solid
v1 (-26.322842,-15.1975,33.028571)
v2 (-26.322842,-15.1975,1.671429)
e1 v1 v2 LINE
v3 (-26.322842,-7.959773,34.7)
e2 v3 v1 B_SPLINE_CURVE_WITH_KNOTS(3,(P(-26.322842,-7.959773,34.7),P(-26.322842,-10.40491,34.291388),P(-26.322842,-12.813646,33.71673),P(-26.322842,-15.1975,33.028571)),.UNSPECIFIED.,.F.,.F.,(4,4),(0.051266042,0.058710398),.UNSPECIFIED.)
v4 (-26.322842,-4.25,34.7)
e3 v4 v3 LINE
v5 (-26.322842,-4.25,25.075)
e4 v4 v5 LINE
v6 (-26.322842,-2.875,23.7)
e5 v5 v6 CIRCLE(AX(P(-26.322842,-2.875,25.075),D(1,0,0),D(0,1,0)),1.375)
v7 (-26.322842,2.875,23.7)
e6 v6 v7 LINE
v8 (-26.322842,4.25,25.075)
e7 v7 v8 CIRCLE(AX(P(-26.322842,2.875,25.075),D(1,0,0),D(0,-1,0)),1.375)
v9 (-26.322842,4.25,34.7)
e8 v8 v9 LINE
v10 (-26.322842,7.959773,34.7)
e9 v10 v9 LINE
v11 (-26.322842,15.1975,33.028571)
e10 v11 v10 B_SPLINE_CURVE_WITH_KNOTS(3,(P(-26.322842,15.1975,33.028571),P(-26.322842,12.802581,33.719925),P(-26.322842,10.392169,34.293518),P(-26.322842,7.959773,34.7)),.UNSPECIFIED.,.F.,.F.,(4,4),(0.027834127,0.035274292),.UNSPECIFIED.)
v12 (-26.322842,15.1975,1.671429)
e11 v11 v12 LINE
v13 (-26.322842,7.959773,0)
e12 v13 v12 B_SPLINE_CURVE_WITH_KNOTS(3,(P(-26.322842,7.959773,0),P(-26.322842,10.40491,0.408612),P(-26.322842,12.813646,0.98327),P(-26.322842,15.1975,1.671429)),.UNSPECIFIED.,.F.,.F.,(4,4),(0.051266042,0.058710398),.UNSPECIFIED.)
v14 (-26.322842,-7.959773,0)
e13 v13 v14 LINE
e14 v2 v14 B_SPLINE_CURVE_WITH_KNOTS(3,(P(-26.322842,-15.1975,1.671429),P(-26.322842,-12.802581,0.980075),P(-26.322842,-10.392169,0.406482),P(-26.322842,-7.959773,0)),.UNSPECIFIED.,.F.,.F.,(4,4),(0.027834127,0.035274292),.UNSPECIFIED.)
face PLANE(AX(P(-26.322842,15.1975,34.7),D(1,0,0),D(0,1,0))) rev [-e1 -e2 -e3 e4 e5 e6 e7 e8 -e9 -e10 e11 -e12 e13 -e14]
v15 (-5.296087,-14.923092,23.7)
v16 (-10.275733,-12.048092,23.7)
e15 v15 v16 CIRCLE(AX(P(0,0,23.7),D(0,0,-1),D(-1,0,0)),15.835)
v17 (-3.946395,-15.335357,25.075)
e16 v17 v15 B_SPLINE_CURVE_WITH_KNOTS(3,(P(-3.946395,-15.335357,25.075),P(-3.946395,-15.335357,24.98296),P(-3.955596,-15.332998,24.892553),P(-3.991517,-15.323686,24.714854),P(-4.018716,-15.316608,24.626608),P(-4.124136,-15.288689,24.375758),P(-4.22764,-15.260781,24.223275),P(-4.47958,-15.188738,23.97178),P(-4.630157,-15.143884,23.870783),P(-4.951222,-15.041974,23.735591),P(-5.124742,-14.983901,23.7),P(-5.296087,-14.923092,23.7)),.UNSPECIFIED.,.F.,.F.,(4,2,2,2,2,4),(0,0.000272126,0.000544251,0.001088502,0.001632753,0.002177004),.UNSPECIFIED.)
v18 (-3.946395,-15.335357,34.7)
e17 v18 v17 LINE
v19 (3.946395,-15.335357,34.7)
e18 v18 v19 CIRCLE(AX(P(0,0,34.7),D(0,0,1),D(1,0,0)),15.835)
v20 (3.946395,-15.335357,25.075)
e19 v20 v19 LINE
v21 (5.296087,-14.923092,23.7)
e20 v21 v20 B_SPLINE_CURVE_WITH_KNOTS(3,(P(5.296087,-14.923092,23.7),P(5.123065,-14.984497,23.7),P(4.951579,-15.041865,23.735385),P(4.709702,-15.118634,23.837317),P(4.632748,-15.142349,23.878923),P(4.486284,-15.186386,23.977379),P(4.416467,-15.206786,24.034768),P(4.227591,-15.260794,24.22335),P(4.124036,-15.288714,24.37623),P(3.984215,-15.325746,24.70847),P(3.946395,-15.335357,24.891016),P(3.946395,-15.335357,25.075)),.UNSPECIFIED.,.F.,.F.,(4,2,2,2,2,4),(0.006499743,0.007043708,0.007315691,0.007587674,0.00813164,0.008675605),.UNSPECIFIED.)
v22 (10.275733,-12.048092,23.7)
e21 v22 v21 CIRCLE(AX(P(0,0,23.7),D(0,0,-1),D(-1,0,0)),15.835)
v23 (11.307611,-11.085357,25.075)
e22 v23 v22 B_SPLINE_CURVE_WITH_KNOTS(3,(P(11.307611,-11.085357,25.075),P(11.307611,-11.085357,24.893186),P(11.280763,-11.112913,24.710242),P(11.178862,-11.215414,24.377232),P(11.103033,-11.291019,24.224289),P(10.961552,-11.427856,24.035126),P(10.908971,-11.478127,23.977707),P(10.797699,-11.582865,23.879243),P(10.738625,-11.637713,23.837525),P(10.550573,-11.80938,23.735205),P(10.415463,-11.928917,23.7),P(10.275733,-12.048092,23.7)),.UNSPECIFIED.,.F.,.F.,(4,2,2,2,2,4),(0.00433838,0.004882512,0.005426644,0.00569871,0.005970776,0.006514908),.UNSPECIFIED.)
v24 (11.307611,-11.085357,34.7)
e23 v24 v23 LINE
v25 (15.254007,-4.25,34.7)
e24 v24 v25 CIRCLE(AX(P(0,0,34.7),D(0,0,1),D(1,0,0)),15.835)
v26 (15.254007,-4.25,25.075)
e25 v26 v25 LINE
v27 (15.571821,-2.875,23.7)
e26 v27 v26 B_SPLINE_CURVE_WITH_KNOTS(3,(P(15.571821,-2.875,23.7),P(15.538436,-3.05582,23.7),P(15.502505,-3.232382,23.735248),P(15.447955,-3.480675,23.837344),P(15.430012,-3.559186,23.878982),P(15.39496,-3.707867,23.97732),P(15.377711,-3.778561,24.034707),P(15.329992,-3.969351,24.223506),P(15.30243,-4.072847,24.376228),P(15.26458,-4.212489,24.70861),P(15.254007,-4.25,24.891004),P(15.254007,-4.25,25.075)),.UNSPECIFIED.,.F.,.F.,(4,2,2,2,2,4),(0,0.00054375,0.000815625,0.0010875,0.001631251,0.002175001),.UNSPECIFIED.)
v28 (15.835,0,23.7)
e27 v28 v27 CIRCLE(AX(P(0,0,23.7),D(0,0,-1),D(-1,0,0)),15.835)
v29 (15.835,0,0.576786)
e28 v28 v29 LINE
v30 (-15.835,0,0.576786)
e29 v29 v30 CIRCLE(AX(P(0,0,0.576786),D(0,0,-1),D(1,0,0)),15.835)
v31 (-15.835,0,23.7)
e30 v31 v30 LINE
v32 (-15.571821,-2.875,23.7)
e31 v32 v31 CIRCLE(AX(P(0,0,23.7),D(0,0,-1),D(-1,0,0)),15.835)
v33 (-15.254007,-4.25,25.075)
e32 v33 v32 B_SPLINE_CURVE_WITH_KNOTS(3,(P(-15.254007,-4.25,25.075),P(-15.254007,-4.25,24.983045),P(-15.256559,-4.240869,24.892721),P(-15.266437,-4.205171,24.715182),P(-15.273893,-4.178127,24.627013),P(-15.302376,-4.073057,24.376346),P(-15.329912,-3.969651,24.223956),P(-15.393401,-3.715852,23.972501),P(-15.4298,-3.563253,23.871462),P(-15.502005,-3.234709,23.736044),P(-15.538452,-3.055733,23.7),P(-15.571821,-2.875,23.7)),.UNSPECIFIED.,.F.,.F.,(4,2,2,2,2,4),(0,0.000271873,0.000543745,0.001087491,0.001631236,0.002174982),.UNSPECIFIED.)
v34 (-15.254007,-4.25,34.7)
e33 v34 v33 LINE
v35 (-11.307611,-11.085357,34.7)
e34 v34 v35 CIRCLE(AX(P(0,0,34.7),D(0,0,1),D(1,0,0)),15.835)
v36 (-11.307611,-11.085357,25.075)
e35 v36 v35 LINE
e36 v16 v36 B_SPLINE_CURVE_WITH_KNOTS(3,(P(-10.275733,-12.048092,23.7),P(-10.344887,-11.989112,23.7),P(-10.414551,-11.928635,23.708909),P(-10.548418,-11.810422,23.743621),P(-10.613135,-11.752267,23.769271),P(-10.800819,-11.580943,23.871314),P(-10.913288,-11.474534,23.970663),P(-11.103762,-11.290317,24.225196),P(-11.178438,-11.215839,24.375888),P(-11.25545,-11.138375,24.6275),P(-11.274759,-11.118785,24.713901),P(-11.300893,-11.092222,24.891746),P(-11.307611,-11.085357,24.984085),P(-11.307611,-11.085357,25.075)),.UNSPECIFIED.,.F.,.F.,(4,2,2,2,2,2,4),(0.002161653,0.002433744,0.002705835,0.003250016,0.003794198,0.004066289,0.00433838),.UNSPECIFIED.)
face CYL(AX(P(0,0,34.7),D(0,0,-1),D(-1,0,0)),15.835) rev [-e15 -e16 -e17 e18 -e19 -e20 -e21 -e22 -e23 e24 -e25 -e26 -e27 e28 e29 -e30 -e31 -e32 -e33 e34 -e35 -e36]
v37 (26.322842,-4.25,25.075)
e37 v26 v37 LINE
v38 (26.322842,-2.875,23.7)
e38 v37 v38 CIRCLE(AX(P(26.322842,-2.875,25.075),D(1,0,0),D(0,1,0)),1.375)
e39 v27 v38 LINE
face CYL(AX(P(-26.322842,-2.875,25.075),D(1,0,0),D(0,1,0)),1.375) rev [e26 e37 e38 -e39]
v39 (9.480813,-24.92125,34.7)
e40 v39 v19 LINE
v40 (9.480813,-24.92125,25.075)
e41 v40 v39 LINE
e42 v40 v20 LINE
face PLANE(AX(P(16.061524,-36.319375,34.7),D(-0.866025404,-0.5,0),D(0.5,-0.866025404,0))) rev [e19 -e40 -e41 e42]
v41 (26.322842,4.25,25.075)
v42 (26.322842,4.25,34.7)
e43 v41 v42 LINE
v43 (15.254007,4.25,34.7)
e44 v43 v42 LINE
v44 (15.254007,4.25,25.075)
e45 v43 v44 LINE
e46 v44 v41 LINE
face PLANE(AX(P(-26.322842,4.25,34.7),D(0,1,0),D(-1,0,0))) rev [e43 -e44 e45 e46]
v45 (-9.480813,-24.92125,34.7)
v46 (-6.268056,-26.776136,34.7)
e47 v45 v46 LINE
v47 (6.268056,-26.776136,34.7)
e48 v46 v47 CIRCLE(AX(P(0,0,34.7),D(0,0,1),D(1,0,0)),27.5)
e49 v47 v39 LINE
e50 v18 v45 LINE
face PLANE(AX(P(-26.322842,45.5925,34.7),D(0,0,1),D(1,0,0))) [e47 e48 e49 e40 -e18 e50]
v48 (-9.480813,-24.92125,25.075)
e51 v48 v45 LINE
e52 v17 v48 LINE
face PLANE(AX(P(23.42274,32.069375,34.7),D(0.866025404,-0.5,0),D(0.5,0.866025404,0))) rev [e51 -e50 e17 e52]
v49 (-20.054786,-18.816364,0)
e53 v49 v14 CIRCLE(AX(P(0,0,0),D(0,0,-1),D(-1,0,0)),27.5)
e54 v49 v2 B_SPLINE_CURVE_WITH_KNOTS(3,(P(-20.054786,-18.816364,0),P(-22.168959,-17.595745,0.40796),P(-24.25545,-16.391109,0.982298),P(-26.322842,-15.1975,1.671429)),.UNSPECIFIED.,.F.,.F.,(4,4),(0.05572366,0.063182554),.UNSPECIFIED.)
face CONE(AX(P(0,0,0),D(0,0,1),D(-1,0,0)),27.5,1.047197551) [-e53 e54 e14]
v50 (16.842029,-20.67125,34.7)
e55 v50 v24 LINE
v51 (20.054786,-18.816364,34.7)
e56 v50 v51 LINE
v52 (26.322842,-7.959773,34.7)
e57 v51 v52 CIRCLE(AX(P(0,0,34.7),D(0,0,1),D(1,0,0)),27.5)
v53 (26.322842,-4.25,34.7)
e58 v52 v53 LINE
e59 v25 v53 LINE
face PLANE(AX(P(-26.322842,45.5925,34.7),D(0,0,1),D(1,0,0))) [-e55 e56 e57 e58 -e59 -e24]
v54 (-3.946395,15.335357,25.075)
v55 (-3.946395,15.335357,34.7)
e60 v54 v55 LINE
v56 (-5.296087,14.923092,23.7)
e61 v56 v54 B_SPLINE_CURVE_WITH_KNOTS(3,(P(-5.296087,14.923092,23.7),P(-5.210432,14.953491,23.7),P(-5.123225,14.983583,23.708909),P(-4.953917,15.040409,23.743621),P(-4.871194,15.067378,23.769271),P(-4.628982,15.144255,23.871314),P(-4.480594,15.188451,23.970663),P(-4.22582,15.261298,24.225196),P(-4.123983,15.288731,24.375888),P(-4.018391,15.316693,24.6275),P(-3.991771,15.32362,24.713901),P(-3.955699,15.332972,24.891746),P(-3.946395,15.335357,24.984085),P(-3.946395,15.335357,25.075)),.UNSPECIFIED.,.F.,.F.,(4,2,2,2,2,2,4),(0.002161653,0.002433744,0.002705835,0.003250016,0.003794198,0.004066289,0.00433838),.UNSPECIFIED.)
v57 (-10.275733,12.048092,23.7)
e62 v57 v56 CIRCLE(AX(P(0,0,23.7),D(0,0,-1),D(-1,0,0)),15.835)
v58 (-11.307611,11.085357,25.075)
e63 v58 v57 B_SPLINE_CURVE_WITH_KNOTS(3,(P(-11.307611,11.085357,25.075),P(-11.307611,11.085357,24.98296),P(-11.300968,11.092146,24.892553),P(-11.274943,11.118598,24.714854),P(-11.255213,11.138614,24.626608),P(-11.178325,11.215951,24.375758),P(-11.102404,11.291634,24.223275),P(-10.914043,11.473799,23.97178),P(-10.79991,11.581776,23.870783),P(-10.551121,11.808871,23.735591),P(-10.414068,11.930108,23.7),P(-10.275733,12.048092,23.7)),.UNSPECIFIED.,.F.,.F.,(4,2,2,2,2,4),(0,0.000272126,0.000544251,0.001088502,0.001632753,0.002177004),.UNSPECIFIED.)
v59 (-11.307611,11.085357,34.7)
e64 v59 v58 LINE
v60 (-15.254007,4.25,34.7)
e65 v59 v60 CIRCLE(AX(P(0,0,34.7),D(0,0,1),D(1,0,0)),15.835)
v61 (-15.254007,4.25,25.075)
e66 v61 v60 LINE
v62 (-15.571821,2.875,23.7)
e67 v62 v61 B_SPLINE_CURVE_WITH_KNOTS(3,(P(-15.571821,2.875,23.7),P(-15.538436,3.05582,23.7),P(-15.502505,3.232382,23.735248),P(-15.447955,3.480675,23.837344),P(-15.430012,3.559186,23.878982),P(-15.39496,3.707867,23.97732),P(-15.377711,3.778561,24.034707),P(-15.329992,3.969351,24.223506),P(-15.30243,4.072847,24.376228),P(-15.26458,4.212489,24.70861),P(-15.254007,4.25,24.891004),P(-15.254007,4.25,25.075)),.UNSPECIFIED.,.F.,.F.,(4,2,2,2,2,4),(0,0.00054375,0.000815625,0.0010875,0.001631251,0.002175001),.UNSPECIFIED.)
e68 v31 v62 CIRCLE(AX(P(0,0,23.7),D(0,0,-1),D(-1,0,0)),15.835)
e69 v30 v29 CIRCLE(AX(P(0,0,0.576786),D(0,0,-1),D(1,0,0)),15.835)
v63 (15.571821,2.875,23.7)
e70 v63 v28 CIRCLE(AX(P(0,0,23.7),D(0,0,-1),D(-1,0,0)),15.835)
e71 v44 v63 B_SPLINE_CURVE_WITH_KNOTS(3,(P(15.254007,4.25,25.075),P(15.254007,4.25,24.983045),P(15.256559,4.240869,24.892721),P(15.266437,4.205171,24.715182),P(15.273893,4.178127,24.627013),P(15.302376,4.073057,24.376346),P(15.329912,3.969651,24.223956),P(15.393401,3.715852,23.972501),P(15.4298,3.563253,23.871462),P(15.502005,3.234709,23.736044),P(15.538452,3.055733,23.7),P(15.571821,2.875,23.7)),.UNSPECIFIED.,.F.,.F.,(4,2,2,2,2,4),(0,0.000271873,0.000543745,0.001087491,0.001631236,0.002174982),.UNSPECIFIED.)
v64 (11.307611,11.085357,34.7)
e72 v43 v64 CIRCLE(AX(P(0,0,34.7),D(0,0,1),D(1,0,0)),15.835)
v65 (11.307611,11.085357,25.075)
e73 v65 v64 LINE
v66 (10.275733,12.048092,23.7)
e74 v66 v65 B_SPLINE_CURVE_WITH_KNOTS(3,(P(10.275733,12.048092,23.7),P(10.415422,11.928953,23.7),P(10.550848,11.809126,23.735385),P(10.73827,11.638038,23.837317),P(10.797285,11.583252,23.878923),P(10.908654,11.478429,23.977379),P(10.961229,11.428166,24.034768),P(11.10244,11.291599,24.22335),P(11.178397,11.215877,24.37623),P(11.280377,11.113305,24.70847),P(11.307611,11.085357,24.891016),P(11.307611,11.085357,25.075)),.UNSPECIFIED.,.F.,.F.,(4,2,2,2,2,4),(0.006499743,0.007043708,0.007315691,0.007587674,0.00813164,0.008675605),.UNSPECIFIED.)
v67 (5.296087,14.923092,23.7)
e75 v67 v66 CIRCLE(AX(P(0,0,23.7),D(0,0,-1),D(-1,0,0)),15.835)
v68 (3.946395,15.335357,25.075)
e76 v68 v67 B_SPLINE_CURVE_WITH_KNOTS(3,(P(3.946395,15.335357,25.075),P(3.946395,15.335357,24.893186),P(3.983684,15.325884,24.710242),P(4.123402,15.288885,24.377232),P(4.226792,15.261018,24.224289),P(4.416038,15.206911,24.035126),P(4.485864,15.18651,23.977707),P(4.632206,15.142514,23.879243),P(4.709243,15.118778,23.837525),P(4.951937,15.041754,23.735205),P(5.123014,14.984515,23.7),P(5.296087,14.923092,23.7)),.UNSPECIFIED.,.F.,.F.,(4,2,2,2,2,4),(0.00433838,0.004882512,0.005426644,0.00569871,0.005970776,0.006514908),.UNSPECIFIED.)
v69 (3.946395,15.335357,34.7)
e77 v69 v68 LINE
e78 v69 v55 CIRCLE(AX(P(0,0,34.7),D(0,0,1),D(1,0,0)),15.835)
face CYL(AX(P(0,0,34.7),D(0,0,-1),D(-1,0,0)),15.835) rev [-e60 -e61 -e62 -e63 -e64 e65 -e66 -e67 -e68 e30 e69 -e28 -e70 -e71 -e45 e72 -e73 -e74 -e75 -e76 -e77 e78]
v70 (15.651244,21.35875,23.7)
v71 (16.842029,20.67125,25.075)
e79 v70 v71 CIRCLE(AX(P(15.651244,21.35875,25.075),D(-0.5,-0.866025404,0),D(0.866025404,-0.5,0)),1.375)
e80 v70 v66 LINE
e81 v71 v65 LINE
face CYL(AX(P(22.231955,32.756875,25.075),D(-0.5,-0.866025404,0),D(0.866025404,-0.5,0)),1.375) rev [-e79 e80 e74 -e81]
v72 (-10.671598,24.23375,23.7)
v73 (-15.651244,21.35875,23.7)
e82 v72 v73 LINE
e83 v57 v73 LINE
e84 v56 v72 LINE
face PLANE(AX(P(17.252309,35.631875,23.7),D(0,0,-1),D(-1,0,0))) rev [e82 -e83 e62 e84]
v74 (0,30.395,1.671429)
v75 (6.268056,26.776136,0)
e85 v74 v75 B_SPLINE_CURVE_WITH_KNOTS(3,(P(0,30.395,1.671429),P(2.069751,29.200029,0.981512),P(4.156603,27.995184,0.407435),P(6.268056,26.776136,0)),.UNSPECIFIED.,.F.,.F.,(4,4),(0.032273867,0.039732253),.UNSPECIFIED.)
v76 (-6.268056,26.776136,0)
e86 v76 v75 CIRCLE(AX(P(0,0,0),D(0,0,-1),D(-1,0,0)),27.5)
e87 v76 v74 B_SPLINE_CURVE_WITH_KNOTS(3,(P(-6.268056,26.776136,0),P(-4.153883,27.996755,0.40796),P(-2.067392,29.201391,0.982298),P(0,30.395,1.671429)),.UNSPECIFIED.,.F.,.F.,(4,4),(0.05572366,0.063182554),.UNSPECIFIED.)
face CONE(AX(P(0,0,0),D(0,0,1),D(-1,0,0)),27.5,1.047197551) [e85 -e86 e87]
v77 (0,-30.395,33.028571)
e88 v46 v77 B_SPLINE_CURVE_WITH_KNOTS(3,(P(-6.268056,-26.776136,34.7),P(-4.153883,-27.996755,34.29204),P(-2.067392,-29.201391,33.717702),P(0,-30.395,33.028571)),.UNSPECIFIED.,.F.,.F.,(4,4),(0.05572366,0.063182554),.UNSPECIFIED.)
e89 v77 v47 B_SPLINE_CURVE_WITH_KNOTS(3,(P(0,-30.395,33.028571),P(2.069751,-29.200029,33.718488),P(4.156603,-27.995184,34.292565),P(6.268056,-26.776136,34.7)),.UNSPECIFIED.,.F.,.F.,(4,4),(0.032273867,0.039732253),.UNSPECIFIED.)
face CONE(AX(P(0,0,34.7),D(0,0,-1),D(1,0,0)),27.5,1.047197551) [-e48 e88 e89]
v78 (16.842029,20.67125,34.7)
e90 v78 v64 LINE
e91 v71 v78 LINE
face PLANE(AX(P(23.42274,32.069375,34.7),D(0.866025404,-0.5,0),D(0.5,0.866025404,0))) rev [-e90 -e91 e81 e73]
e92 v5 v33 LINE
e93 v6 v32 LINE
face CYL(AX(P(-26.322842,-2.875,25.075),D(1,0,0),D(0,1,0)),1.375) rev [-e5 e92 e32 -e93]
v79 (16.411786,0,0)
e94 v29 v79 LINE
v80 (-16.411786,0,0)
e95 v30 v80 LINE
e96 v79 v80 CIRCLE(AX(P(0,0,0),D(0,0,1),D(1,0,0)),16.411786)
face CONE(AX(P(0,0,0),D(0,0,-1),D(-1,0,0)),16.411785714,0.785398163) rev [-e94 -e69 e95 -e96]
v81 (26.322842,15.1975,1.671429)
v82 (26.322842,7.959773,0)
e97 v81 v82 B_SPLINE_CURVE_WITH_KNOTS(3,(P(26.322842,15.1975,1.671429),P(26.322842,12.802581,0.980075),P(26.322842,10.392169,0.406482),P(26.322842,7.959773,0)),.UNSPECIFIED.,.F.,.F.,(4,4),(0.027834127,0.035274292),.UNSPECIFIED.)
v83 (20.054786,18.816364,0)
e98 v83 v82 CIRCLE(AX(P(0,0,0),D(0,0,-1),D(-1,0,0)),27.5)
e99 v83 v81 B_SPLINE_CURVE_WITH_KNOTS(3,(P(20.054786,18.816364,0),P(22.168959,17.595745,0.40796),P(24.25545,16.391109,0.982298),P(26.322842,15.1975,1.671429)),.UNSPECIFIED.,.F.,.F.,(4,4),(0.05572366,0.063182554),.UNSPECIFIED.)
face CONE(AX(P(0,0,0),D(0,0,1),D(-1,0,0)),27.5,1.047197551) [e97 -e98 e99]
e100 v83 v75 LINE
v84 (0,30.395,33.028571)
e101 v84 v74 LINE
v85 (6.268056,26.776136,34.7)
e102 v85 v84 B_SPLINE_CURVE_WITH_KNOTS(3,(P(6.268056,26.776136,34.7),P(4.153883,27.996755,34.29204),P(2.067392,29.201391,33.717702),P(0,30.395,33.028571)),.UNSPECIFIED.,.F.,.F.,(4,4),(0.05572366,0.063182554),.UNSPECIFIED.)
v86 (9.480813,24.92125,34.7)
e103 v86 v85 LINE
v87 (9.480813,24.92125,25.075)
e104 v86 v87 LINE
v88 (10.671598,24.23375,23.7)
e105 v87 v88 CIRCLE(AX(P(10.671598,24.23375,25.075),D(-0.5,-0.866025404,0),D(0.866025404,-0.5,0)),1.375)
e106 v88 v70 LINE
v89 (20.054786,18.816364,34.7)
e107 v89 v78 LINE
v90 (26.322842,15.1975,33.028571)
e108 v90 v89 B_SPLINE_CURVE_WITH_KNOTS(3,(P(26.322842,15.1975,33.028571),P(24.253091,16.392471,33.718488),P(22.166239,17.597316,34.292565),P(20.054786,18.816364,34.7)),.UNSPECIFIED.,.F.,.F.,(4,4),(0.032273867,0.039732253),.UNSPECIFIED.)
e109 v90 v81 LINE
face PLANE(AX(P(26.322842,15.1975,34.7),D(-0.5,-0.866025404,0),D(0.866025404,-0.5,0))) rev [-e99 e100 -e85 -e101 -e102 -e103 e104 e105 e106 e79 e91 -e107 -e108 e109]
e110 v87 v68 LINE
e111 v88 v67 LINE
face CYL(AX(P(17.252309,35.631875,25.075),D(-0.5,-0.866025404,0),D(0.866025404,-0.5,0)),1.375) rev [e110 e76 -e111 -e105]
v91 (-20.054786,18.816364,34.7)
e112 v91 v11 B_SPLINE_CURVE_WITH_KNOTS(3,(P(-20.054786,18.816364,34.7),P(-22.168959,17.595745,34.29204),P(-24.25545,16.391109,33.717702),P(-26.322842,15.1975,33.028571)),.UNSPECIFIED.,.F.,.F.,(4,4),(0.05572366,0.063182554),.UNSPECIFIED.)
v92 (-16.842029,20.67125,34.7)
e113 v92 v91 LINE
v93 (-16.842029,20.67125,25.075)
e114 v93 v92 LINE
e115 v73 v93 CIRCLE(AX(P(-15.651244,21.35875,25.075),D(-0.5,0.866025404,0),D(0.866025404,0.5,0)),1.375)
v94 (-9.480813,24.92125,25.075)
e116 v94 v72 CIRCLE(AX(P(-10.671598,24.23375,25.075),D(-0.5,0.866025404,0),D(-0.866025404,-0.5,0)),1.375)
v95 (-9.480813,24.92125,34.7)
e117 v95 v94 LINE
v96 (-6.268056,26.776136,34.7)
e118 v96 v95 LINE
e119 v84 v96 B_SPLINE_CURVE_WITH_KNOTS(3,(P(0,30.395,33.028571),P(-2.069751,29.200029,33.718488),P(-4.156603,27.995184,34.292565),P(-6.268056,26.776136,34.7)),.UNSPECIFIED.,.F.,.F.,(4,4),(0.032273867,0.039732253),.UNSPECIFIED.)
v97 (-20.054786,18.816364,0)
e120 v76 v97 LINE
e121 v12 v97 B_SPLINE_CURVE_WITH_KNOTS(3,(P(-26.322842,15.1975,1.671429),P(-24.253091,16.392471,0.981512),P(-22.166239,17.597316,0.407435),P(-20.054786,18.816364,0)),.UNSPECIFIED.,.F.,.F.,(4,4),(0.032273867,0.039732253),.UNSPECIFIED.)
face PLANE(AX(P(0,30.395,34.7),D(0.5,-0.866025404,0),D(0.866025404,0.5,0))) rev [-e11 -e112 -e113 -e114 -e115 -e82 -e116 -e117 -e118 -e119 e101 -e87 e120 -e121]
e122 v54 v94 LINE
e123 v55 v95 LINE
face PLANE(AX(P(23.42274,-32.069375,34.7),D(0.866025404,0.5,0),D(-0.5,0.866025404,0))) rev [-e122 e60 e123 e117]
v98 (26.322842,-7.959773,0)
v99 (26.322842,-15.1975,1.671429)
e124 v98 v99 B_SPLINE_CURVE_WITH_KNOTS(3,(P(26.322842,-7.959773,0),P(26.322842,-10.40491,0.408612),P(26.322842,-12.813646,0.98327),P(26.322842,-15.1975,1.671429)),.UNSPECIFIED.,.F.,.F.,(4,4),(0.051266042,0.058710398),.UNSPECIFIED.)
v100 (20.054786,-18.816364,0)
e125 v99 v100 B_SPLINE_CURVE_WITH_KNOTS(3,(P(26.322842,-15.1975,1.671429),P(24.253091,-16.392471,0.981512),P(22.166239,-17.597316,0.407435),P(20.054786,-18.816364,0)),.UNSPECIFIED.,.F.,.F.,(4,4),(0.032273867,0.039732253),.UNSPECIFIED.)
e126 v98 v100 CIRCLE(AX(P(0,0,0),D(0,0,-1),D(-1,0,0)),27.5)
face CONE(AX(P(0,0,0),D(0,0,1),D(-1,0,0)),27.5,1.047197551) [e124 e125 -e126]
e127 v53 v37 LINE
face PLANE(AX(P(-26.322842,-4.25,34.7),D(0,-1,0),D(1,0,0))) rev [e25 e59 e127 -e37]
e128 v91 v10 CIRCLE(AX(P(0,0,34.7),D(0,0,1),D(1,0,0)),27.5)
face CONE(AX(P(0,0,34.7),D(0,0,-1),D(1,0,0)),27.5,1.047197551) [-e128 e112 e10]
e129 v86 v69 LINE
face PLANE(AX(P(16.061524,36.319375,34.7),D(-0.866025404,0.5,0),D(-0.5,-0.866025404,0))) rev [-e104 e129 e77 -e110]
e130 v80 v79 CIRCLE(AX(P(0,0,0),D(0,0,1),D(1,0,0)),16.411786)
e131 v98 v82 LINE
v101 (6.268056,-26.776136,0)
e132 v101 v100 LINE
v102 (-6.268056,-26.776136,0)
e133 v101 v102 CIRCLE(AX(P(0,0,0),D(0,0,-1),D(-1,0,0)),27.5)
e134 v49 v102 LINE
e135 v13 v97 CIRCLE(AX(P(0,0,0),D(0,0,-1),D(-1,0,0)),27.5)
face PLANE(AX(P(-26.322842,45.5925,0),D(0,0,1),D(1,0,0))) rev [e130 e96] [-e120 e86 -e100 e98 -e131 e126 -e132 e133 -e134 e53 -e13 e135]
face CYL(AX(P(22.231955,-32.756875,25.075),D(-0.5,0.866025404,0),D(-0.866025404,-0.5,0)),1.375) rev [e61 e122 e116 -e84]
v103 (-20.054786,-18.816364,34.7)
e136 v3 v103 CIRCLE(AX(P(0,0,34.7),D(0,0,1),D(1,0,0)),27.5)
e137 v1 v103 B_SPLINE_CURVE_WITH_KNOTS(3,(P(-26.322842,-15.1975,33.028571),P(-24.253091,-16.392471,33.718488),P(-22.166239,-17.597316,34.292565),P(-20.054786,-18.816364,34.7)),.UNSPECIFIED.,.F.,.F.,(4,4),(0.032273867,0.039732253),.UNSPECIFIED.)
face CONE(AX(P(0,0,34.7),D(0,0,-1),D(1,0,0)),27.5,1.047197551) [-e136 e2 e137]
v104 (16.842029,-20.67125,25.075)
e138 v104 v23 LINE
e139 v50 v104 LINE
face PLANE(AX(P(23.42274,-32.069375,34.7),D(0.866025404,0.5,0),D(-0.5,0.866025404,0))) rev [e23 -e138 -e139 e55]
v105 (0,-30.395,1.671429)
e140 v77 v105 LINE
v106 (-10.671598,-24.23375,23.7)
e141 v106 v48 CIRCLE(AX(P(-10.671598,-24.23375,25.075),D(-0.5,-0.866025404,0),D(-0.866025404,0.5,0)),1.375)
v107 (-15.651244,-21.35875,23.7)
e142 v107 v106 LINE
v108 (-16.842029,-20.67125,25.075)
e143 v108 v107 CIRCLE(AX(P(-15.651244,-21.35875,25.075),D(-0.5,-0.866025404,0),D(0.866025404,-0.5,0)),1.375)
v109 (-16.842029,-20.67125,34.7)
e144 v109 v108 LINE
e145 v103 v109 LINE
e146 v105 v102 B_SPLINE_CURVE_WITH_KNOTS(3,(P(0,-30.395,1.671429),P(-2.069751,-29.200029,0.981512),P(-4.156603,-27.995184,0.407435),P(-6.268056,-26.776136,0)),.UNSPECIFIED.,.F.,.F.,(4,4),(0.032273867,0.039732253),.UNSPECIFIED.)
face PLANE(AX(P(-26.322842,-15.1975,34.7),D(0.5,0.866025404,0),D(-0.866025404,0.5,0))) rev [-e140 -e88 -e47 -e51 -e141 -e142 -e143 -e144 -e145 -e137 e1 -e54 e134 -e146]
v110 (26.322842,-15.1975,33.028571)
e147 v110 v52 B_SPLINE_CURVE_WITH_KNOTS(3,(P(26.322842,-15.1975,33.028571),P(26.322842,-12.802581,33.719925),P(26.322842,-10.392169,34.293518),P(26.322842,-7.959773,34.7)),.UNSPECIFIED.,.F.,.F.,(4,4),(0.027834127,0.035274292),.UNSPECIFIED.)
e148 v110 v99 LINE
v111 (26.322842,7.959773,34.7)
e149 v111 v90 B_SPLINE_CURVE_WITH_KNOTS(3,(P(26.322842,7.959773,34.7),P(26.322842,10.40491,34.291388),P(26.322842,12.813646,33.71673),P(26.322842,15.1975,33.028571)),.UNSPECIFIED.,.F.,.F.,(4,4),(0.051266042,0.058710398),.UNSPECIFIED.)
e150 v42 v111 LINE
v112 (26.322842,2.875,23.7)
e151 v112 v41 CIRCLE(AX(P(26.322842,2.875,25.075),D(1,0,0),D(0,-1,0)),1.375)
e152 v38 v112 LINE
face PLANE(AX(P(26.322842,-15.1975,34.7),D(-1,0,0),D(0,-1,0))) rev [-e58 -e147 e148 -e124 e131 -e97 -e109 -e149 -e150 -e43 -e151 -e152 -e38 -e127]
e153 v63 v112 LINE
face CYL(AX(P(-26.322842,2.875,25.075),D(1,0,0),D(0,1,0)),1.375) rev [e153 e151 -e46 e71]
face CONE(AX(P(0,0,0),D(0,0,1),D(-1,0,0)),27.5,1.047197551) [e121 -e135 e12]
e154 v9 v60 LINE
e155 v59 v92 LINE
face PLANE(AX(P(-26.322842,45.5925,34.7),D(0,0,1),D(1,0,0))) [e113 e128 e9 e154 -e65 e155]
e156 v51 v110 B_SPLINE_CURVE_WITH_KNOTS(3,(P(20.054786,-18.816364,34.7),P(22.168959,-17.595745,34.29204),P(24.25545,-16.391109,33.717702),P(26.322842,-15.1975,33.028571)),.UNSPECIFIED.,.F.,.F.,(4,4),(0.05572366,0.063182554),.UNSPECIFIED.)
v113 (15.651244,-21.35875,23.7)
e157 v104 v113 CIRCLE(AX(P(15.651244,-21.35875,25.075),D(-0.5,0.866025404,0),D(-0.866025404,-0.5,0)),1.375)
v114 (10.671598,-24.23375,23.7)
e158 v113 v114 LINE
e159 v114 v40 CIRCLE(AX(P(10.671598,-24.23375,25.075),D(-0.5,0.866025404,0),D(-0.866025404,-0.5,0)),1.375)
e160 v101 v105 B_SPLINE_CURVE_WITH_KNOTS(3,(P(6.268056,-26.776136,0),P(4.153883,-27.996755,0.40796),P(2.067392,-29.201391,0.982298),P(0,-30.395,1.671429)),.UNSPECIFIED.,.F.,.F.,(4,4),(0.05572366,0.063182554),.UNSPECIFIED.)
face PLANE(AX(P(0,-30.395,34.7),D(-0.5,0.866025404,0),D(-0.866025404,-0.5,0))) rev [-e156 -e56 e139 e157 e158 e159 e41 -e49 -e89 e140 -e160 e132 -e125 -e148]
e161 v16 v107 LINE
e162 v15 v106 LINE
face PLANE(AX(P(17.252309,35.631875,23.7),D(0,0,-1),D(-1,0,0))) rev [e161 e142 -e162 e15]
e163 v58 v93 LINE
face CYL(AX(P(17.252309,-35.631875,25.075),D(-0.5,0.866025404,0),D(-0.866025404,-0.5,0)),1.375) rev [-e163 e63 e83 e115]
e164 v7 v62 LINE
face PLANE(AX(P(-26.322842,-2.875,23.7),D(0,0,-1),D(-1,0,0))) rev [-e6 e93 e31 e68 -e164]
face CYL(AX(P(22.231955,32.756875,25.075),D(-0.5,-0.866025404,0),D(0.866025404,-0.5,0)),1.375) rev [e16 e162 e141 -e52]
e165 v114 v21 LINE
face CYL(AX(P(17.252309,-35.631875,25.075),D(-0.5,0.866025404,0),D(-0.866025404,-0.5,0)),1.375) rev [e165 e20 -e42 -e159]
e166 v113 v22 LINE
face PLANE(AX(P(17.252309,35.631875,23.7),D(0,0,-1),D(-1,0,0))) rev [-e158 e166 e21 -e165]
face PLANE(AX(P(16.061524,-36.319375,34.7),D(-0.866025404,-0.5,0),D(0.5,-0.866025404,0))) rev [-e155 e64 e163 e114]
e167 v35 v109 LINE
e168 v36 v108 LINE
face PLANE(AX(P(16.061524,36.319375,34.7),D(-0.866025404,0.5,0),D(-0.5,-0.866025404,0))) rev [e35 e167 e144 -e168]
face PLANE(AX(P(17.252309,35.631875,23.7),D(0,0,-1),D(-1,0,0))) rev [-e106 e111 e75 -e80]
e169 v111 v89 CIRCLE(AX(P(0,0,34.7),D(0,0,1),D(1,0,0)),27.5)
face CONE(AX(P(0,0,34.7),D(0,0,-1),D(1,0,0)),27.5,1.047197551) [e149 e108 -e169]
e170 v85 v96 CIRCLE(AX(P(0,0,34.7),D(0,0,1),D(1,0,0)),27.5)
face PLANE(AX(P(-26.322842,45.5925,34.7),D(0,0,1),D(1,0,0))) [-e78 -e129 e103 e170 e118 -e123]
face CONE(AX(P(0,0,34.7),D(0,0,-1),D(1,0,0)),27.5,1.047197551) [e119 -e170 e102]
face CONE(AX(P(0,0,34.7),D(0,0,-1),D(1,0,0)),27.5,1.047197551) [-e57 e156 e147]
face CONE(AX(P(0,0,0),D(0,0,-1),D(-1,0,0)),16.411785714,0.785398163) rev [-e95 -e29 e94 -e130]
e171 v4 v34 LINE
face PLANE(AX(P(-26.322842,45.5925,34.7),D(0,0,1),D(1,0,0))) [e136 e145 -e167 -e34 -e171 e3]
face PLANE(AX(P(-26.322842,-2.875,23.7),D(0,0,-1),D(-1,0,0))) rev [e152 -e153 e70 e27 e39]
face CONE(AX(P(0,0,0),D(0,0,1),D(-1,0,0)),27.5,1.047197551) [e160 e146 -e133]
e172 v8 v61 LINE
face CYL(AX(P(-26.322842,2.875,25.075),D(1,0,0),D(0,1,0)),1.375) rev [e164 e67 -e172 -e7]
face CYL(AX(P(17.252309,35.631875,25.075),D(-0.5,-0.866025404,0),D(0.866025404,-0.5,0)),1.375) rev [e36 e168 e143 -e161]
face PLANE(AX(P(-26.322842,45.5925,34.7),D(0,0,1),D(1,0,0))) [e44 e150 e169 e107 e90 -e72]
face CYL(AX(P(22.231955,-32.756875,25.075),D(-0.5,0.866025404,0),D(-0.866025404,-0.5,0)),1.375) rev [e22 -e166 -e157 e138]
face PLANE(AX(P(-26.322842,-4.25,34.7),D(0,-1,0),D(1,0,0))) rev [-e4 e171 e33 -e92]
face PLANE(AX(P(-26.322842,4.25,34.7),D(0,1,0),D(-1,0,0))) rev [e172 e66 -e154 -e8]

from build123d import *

# Parameters (mm, degrees)
SKETCH_1_R               = 15.835
EXTRUDE_848_DEPTH        = 34.7
SKETCH_2_OUTSIDE_W       = 259.61
SKETCH_2_OUTSIDE_H       = 267.754
SKETCH_2_OUTSIDE_R       = 27.5
CUT_EXTRUDE_1_DEPTH      = 54.111562242
CUT_EXTRUDE_1_DRAFT      = -60
SKETCH_3_OUTSIDE_W       = 259.61
SKETCH_3_OUTSIDE_H       = 267.754
SKETCH_3_OUTSIDE_R       = 27.5
CUT_EXTRUDE_2_DEPTH      = 54.111562242
CUT_EXTRUDE_2_DRAFT      = -60
CUT_EXTRUDE_3_DEPTH      = 70.9965292
PATTERN_CIRCULAR_1_COUNT = 3
CHAMFER_1_SIZE           = 0.576785714


with BuildPart() as part:
    # 草图1 → Extrude 848 (new body)
    with BuildSketch(Plane.XY):
        Polygon((0, 30.395), (-26.322842148, 15.1975), (-26.322842148, -15.1975), (0, -30.395), (26.322842148, -15.1975), (26.322842148, 15.1975), align=None)
        Circle(SKETCH_1_R, mode=Mode.SUBTRACT)
    extrude(amount=EXTRUDE_848_DEPTH)


with BuildPart() as cut_extrude_1_tool:
    # 草图2 outside → 切除-拉伸1 (with draft: the straight prism first)
    with BuildSketch(Plane(origin=(0, 0, 0), x_dir=(-1, 0, 0), z_dir=(0, 0, -1))):
        Rectangle(SKETCH_2_OUTSIDE_W, SKETCH_2_OUTSIDE_H)
        Circle(SKETCH_2_OUTSIDE_R, mode=Mode.SUBTRACT)
    extrude(amount=-CUT_EXTRUDE_1_DEPTH)
    # 切除-拉伸1: the draft: its side faces are tilted about the plane it starts from
    cut_extrude_1_sides = [cut_extrude_1_tool.faces().sort_by_distance(p)[0] for p in [
        (0, -133.877, 27.055781121),
        (-129.805, 0, 27.055781121),
        (0, 133.877, 27.055781121),
        (129.805, 0, 27.055781121),
        (27.5, 0, 27.055781121),
    ]]
    draft(cut_extrude_1_sides, Plane(origin=(0, 0, 0), x_dir=(-1, 0, 0), z_dir=(0, 0, -1)), CUT_EXTRUDE_1_DRAFT)


with BuildPart() as part_1:
    add(part.part)

    # 切除-拉伸1: cut by cut_extrude_1_tool
    add(cut_extrude_1_tool.part, mode=Mode.SUBTRACT)


with BuildPart() as cut_extrude_2_tool:
    # 草图3 outside → 切除-拉伸2 (with draft: the straight prism first)
    with BuildSketch(Plane.XY.offset(34.7)):
        Rectangle(SKETCH_3_OUTSIDE_W, SKETCH_3_OUTSIDE_H)
        Circle(SKETCH_3_OUTSIDE_R, mode=Mode.SUBTRACT)
    extrude(amount=-CUT_EXTRUDE_2_DEPTH)
    # 切除-拉伸2: the draft: its side faces are tilted about the plane it starts from
    cut_extrude_2_sides = [cut_extrude_2_tool.faces().sort_by_distance(p)[0] for p in [
        (0, -133.877, 7.644218879),
        (129.805, 0, 7.644218879),
        (0, 133.877, 7.644218879),
        (-129.805, 0, 7.644218879),
        (-27.5, 0, 7.644218879),
    ]]
    draft(cut_extrude_2_sides, Plane.XY.offset(34.7), CUT_EXTRUDE_2_DRAFT)


with BuildPart() as part_2:
    add(part_1.part)

    # 切除-拉伸2: cut by cut_extrude_2_tool
    add(cut_extrude_2_tool.part, mode=Mode.SUBTRACT)

    # 草图6 → 切除-拉伸3 (cut, through all)
    with BuildSketch(Plane(origin=(26.322842148, 0, 0), x_dir=(0, 0, -1), z_dir=(1, 0, 0))):
        with BuildLine():
            Line((-34.7, -4.25), (-34.7, 4.25))
            Line((-34.7, 4.25), (-25.075, 4.25))
            ThreePointArc((-25.075, 4.25), (-24.102728176, 3.847271824), (-23.7, 2.875))
            Line((-23.7, 2.875), (-23.7, -2.875))
            ThreePointArc((-23.7, -2.875), (-24.102728176, -3.847271824), (-25.075, -4.25))
            Line((-25.075, -4.25), (-34.7, -4.25))
        make_face()
    cut_extrude_3 = extrude(amount=-CUT_EXTRUDE_3_DEPTH, mode=Mode.SUBTRACT)

    # 阵列(圆周)1: 切除-拉伸3 ×3 about axis
    pattern_circular_1_axis = Axis((0, 0, 0), (0, 0, 1))
    for i in range(1, PATTERN_CIRCULAR_1_COUNT):
        add(cut_extrude_3.rotate(pattern_circular_1_axis, i * 360 / PATTERN_CIRCULAR_1_COUNT), mode=Mode.SUBTRACT)

    # 倒角1
    chamfer_1_edges = [part_2.edges().sort_by_distance(p)[0] for p in [
        (-15.835, 0, 0),
    ]]
    chamfer(chamfer_1_edges, length=CHAMFER_1_SIZE)


solid = part_2.part
